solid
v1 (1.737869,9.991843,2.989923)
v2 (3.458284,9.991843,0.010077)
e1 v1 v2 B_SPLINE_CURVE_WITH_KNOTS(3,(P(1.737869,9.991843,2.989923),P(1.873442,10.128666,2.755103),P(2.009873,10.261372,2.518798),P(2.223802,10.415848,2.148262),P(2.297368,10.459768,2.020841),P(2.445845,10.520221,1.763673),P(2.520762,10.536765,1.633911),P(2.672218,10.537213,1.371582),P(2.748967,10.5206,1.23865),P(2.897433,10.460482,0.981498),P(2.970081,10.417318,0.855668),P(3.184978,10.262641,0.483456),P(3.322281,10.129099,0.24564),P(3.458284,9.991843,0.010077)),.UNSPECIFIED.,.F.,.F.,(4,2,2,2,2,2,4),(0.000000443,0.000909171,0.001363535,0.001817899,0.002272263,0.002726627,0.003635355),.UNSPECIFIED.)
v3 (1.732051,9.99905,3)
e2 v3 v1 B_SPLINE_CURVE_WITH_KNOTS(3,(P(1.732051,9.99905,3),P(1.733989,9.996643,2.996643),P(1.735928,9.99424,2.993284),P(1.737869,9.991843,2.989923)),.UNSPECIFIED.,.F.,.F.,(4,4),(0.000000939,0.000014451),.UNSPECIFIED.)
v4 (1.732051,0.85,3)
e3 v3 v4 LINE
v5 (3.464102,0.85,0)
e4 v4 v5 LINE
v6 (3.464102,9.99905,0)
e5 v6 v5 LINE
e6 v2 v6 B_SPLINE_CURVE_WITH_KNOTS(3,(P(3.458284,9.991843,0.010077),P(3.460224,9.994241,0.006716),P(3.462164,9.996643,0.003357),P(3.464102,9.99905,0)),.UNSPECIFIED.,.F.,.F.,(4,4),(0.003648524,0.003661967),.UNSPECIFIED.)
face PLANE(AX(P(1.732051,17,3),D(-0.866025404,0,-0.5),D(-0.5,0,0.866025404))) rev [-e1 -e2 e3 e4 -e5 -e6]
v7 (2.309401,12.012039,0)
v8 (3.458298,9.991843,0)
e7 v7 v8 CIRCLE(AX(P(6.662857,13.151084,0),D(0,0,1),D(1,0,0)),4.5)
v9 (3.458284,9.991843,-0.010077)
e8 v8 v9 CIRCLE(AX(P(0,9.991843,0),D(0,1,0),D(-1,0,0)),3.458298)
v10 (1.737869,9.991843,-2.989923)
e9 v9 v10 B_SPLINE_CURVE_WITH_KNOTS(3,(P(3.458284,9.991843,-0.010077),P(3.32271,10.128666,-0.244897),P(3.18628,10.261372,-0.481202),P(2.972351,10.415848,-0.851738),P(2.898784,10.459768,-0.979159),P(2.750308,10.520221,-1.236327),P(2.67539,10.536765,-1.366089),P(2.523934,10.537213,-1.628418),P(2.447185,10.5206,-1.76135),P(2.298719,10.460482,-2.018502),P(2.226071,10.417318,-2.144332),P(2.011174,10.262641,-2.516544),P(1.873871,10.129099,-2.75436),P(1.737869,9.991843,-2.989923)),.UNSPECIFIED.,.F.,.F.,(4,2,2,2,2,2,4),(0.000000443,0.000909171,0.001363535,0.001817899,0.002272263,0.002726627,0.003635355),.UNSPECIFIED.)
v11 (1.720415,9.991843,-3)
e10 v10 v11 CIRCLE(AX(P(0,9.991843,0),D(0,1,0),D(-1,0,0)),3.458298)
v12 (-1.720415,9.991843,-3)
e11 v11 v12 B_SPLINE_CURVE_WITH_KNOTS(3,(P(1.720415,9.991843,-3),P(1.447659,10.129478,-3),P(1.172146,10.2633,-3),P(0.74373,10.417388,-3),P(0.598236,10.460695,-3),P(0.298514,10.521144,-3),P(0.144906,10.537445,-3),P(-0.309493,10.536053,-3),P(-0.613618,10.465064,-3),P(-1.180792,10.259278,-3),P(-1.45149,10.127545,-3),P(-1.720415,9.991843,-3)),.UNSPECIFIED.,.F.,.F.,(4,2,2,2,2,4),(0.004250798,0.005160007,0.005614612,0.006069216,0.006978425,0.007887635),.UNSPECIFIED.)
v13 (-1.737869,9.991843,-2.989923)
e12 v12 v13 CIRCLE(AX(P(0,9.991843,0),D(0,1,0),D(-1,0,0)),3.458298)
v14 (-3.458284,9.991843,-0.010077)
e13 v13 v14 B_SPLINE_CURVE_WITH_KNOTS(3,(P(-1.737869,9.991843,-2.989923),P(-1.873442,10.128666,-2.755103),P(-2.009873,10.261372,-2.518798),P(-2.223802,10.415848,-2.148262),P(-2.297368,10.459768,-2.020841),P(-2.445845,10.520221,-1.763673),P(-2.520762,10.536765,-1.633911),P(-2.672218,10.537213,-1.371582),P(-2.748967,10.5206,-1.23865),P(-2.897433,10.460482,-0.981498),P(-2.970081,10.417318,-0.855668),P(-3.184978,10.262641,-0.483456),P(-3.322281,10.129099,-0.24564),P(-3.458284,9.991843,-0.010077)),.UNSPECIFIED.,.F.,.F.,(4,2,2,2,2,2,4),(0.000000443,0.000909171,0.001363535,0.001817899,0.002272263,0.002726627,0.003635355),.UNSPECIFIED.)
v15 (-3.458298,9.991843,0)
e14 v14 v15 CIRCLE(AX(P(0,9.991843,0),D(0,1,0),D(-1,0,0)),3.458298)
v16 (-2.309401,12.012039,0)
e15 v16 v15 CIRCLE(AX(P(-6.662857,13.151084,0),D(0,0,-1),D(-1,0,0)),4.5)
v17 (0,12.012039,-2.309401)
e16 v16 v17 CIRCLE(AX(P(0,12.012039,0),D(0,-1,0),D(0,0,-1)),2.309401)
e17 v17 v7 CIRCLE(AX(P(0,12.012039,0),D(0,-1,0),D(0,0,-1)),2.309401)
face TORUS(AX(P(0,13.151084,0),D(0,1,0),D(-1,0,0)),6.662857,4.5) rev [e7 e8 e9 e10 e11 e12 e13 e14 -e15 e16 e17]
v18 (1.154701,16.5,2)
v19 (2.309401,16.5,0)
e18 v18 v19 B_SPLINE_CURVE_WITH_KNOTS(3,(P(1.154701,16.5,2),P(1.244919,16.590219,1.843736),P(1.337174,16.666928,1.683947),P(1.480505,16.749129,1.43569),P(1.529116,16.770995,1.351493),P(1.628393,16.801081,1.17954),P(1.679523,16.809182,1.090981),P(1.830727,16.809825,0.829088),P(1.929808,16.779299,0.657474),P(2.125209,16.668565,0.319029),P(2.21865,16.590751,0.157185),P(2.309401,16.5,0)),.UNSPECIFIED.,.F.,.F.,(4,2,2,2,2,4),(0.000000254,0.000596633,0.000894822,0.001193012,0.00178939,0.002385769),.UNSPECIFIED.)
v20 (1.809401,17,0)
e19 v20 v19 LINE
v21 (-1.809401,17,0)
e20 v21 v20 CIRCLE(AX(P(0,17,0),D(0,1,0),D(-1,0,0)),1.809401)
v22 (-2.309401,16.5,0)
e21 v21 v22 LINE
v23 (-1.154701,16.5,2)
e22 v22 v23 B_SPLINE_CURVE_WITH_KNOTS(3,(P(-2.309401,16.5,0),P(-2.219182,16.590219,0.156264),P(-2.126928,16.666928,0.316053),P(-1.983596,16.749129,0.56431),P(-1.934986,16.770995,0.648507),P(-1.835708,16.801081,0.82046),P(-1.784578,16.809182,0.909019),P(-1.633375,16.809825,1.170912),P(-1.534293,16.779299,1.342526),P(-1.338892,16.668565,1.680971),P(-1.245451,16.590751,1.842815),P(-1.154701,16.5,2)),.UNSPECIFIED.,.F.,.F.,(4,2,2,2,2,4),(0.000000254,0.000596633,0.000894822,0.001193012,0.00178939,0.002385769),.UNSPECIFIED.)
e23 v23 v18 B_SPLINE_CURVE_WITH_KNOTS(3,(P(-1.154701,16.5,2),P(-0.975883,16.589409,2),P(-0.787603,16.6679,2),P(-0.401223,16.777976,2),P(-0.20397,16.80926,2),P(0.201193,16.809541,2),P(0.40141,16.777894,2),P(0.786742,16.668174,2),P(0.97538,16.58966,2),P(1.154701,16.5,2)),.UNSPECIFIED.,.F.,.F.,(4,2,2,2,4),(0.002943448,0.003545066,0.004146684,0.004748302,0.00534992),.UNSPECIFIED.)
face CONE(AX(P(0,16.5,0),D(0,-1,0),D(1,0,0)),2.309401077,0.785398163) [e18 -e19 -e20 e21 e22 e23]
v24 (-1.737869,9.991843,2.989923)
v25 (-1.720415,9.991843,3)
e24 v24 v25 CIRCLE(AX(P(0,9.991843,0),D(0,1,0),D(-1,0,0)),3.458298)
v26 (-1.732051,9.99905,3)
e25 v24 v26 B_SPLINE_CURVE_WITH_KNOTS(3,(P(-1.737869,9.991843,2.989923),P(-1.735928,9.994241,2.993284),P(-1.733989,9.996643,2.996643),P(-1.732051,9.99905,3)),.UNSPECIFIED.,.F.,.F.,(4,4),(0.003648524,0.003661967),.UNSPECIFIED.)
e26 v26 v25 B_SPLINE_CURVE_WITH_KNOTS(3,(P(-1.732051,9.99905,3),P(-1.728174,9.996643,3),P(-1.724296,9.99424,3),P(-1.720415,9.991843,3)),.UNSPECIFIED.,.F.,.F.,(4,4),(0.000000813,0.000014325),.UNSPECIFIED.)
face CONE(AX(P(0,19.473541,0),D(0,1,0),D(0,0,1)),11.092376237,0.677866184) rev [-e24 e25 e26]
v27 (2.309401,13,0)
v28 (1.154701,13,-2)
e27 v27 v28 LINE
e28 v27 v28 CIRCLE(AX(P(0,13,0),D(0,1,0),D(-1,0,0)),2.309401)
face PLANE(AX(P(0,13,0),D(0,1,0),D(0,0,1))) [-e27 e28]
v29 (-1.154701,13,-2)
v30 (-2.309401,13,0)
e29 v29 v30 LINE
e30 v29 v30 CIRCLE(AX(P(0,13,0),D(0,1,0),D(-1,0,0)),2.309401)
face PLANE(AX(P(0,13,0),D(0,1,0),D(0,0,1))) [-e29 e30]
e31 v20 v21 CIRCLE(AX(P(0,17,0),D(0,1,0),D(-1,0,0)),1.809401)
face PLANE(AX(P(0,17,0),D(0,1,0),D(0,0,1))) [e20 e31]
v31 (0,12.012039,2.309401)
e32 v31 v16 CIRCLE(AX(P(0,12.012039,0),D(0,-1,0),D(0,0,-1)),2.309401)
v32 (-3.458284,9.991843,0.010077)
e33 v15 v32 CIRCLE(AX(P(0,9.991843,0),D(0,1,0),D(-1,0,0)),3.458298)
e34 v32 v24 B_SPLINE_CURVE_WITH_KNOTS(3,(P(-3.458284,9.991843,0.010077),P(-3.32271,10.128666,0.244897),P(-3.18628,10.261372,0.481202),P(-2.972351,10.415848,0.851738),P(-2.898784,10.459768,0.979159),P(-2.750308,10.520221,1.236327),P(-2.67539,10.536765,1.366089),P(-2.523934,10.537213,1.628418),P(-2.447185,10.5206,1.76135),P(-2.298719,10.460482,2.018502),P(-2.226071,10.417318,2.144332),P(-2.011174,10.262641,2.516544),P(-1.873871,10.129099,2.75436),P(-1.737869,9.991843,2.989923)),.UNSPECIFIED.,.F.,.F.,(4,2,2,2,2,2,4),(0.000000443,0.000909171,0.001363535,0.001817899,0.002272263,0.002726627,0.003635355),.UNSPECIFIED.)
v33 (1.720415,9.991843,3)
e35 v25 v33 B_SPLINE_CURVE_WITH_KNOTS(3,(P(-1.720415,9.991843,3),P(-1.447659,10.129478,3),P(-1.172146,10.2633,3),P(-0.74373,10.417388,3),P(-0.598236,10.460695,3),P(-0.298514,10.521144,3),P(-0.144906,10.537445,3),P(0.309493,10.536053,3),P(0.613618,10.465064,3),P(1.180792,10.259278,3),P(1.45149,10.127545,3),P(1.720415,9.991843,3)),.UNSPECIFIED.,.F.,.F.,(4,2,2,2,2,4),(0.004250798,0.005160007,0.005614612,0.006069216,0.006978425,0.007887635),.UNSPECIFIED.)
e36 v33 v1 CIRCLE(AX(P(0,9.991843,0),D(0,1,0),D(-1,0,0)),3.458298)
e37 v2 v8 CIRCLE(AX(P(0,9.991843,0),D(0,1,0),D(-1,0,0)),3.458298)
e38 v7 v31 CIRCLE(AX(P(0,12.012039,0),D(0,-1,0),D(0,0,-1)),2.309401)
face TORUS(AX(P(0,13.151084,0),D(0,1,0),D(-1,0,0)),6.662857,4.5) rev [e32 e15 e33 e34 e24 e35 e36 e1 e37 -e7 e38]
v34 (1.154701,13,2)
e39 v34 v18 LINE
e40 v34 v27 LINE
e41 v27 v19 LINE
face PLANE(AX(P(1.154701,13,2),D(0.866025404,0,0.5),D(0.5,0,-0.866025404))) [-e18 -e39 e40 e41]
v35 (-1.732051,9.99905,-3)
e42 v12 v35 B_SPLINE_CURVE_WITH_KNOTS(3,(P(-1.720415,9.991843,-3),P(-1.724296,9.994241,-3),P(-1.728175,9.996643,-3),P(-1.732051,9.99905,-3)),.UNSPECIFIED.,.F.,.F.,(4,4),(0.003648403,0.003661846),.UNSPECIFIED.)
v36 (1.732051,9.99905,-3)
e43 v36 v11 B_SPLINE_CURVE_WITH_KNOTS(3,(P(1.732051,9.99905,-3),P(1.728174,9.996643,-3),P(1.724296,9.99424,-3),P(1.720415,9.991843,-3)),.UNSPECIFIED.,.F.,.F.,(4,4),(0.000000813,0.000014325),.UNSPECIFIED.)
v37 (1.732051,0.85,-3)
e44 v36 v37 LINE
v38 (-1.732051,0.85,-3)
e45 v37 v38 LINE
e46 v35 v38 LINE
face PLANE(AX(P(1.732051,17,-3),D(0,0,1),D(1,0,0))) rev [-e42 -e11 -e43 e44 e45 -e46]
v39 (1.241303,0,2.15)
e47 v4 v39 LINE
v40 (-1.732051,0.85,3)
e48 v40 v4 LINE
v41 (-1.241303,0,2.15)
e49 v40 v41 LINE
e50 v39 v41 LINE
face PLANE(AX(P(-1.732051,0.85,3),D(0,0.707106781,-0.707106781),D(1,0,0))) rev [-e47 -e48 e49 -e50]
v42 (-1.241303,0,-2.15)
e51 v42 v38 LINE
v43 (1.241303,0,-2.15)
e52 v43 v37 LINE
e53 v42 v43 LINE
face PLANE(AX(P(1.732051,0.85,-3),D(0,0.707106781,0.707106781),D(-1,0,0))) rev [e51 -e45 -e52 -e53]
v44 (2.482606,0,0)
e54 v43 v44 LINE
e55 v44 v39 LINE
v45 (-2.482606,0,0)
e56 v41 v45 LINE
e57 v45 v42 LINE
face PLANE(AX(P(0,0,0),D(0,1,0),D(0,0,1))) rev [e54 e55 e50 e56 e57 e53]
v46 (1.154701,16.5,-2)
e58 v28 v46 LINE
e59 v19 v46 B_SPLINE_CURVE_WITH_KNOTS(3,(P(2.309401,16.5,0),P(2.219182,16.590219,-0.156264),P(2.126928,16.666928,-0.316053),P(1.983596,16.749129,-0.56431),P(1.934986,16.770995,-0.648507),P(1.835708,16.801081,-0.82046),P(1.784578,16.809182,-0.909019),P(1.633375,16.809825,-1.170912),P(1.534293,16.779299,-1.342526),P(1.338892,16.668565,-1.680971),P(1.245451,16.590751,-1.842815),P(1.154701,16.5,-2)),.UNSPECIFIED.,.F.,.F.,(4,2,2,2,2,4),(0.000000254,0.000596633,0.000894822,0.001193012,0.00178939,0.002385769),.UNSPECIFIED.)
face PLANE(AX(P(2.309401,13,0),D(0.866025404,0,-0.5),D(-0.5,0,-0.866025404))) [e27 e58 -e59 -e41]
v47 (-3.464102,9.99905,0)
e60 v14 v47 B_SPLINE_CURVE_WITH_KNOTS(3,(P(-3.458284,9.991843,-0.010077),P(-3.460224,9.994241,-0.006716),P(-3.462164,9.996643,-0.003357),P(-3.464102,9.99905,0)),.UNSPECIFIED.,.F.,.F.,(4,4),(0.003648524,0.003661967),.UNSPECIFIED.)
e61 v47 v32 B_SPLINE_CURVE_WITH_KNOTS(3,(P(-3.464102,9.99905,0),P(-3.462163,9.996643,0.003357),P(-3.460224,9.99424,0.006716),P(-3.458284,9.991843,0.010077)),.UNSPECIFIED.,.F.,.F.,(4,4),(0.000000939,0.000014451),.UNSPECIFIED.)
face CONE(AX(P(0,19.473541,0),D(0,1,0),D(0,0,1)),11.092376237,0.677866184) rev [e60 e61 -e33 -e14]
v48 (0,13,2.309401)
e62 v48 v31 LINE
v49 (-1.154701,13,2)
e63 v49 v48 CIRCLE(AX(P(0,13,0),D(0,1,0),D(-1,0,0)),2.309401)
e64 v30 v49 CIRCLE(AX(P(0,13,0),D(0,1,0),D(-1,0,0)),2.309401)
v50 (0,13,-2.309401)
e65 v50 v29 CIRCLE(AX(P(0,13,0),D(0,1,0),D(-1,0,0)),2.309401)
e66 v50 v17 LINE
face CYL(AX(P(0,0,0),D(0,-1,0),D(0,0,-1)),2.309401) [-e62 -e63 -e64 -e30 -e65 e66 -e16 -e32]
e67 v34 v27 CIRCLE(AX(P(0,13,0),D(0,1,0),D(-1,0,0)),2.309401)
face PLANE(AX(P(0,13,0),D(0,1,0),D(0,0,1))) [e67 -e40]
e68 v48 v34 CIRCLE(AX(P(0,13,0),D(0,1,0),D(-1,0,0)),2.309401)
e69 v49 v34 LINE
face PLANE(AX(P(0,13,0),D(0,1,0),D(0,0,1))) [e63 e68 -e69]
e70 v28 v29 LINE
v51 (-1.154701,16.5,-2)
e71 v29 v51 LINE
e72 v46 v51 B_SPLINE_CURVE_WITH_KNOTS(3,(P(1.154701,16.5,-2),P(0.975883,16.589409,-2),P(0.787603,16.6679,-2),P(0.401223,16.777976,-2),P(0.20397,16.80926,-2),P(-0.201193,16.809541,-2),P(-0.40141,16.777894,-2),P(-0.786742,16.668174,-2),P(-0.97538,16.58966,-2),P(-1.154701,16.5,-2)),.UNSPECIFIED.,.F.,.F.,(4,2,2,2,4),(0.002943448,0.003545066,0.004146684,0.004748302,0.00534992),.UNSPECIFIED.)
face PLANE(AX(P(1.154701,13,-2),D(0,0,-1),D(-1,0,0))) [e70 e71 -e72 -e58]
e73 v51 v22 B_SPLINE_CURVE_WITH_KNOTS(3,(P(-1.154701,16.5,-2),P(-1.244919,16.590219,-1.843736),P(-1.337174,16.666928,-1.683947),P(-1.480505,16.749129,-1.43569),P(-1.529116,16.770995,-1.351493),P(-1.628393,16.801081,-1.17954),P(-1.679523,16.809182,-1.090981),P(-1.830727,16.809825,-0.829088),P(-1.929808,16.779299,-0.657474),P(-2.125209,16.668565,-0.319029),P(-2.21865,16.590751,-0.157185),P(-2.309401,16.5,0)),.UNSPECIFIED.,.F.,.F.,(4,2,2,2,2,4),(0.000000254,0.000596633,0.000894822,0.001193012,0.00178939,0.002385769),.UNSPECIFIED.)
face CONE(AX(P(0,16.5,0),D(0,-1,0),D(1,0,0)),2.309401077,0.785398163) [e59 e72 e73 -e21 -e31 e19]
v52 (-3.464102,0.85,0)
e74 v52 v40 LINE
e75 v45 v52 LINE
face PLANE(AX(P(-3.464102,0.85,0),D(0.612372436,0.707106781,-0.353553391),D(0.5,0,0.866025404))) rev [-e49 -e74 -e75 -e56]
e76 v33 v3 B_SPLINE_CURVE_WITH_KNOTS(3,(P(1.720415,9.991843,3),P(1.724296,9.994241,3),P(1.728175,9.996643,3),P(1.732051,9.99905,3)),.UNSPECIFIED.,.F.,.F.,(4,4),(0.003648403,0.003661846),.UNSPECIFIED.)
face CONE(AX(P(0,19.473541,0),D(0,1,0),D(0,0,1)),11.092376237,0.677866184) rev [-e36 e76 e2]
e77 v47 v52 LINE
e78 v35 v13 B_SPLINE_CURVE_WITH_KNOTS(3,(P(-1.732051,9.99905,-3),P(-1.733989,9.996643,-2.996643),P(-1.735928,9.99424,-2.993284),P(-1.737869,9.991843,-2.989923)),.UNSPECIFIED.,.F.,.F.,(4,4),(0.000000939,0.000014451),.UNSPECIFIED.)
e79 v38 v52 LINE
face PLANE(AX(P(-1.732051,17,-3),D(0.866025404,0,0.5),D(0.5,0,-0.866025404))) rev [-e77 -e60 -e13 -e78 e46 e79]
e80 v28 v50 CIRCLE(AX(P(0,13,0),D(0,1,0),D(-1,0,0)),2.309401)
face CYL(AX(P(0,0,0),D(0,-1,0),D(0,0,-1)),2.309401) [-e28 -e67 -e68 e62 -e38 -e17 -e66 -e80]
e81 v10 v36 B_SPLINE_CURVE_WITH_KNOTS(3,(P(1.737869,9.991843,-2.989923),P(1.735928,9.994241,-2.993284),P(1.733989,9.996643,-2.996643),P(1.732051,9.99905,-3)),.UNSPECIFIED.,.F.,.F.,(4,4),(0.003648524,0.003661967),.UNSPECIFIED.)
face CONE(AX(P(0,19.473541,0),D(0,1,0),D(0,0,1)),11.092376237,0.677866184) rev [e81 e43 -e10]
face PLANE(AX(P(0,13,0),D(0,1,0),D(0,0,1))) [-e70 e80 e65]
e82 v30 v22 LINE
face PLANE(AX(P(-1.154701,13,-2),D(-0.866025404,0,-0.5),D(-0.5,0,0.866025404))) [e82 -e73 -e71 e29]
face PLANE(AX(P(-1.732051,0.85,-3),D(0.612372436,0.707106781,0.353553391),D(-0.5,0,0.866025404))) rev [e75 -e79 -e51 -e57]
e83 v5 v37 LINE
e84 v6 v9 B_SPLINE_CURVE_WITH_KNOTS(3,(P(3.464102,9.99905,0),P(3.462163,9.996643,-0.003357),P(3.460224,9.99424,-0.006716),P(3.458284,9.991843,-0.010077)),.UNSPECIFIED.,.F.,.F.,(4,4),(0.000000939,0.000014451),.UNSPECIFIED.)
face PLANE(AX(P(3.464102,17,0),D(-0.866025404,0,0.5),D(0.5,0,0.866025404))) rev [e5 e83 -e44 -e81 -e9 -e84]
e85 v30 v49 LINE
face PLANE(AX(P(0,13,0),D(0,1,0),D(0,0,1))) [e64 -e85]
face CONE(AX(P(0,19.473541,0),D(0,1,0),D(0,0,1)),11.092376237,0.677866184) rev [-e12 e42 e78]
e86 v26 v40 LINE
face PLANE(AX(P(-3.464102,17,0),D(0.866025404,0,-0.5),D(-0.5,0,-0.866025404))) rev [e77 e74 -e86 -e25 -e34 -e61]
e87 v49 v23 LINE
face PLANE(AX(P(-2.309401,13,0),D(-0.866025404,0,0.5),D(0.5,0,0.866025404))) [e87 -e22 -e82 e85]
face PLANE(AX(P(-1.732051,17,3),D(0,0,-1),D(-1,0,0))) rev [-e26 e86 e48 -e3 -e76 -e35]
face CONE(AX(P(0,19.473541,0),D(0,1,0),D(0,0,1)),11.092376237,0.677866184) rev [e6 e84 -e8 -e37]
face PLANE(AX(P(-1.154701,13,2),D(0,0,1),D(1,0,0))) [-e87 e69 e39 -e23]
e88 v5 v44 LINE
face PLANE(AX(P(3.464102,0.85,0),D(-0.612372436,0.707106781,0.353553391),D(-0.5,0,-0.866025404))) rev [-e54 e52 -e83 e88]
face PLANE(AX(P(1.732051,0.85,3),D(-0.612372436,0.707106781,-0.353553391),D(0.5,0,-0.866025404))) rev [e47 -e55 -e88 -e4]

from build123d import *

# Parameters (mm, degrees)
HEX_BODY_6AF_X17_DEPTH        = 17
EDGE_CHAMFER_0_85_SIZE        = 0.85
HEX_TIP_PROFILE_4AF_OUTSIDE_W = 12.79
HEX_TIP_PROFILE_4AF_OUTSIDE_H = 11.862
HEX_TIP_4AF_X4_DEPTH          = 4


with BuildPart() as part:
    # Hex Body Profile 6AF → Hex Body 6AF x17 (new body)
    with BuildSketch(Plane(origin=(0, 0, 0), x_dir=(1, 0, 0), z_dir=(0, 1, 0))):
        Polygon((3.464101615, 0), (1.732050808, 3), (-1.732050808, 3), (-3.464101615, 0), (-1.732050808, -3), (1.732050808, -3), align=None)
    extrude(amount=HEX_BODY_6AF_X17_DEPTH)

    # Edge Chamfer 0.85
    edge_chamfer_0_85_edges = [part.edges().sort_by_distance(p)[0] for p in [
        (0, 0, 3),
        (-2.598076211, 0, 1.5),
        (-2.598076211, 0, -1.5),
        (0, 0, -3),
        (2.598076211, 0, -1.5),
        (2.598076211, 0, 1.5),
    ]]
    chamfer(edge_chamfer_0_85_edges, length=EDGE_CHAMFER_0_85_SIZE)

    # Hex Tip Profile 4AF outside → Hex Tip 4AF x4 (cut)
    with BuildSketch(Plane(origin=(0, 17, 0), x_dir=(1, 0, 0), z_dir=(0, 1, 0))):
        Rectangle(HEX_TIP_PROFILE_4AF_OUTSIDE_W, HEX_TIP_PROFILE_4AF_OUTSIDE_H)
        Polygon((2.309401077, 0), (1.154700538, 2), (-1.154700538, 2), (-2.309401077, 0), (-1.154700538, -2), (1.154700538, -2), align=None, mode=Mode.SUBTRACT)
    extrude(amount=-HEX_TIP_4AF_X4_DEPTH, mode=Mode.SUBTRACT)

    # Neck Groove Profile → Neck Groove (revolve, cut)
    with BuildSketch(Plane.XY):
        with BuildLine():
            Line((-3.464101615, 12.012038592), (-3.464101615, 13))
            Line((-3.464101615, 13), (-2.309401077, 13))
            ThreePointArc((-2.309401077, 13), (-2.659285909, 12.240164314), (-3.464101615, 12.012038592))
        make_face()
        with BuildLine():
            ThreePointArc((2.309401077, 12.012038592), (2.751182948, 10.926492222), (3.458298406, 9.991842624))
            Line((3.458298406, 9.991842624), (3.458298406, 12.012038592))
            Line((3.458298406, 12.012038592), (2.309401077, 12.012038592))
        make_face()
    revolve(axis=Axis((0, 17, 0), (0, -1, 0)), mode=Mode.SUBTRACT)

    # Hex Corner Turn Profile → Hex Corner Turn (revolve, cut)
    with BuildSketch(Plane.XY, mode=Mode.PRIVATE) as hex_corner_turn_sk:
        with BuildLine():
            Line((2.309401077, 16.837685955), (2.309401077, 13))
            Line((2.309401077, 13), (2.309401077, 12.012038592))
            ThreePointArc((2.309401077, 12.012038592), (2.751182948, 10.926492222), (3.458298406, 9.991842624))
            Line((3.458298406, 9.991842624), (11.092376237, 19.473540628))
            Line((11.092376237, 19.473540628), (2.309401077, 19.67629868))
            Line((2.309401077, 19.67629868), (2.309401077, 17))
            Line((2.309401077, 17), (2.309401077, 16.837685955))
        make_face()
    revolve(hex_corner_turn_sk.sketch.rotate(Axis((0, 0, 0), (0, 1, 0)), 179.8330498), axis=Axis((0, 0, 0), (0, 1, 0)), mode=Mode.SUBTRACT)

    # Tip Chamfer Profile → Tip Chamfer 0.5x45 (revolve, cut)
    with BuildSketch(Plane.XY, mode=Mode.PRIVATE) as tip_chamfer_0_5x45_sk:
        Polygon((-1.809401077, 17), (-2.309401077, 17), (-2.309401077, 16.5), align=None)
    revolve(tip_chamfer_0_5x45_sk.sketch.rotate(Axis((0, 17, 0), (0, -1, 0)), 90), axis=Axis((0, 17, 0), (0, -1, 0)), mode=Mode.SUBTRACT)


solid = part.part
